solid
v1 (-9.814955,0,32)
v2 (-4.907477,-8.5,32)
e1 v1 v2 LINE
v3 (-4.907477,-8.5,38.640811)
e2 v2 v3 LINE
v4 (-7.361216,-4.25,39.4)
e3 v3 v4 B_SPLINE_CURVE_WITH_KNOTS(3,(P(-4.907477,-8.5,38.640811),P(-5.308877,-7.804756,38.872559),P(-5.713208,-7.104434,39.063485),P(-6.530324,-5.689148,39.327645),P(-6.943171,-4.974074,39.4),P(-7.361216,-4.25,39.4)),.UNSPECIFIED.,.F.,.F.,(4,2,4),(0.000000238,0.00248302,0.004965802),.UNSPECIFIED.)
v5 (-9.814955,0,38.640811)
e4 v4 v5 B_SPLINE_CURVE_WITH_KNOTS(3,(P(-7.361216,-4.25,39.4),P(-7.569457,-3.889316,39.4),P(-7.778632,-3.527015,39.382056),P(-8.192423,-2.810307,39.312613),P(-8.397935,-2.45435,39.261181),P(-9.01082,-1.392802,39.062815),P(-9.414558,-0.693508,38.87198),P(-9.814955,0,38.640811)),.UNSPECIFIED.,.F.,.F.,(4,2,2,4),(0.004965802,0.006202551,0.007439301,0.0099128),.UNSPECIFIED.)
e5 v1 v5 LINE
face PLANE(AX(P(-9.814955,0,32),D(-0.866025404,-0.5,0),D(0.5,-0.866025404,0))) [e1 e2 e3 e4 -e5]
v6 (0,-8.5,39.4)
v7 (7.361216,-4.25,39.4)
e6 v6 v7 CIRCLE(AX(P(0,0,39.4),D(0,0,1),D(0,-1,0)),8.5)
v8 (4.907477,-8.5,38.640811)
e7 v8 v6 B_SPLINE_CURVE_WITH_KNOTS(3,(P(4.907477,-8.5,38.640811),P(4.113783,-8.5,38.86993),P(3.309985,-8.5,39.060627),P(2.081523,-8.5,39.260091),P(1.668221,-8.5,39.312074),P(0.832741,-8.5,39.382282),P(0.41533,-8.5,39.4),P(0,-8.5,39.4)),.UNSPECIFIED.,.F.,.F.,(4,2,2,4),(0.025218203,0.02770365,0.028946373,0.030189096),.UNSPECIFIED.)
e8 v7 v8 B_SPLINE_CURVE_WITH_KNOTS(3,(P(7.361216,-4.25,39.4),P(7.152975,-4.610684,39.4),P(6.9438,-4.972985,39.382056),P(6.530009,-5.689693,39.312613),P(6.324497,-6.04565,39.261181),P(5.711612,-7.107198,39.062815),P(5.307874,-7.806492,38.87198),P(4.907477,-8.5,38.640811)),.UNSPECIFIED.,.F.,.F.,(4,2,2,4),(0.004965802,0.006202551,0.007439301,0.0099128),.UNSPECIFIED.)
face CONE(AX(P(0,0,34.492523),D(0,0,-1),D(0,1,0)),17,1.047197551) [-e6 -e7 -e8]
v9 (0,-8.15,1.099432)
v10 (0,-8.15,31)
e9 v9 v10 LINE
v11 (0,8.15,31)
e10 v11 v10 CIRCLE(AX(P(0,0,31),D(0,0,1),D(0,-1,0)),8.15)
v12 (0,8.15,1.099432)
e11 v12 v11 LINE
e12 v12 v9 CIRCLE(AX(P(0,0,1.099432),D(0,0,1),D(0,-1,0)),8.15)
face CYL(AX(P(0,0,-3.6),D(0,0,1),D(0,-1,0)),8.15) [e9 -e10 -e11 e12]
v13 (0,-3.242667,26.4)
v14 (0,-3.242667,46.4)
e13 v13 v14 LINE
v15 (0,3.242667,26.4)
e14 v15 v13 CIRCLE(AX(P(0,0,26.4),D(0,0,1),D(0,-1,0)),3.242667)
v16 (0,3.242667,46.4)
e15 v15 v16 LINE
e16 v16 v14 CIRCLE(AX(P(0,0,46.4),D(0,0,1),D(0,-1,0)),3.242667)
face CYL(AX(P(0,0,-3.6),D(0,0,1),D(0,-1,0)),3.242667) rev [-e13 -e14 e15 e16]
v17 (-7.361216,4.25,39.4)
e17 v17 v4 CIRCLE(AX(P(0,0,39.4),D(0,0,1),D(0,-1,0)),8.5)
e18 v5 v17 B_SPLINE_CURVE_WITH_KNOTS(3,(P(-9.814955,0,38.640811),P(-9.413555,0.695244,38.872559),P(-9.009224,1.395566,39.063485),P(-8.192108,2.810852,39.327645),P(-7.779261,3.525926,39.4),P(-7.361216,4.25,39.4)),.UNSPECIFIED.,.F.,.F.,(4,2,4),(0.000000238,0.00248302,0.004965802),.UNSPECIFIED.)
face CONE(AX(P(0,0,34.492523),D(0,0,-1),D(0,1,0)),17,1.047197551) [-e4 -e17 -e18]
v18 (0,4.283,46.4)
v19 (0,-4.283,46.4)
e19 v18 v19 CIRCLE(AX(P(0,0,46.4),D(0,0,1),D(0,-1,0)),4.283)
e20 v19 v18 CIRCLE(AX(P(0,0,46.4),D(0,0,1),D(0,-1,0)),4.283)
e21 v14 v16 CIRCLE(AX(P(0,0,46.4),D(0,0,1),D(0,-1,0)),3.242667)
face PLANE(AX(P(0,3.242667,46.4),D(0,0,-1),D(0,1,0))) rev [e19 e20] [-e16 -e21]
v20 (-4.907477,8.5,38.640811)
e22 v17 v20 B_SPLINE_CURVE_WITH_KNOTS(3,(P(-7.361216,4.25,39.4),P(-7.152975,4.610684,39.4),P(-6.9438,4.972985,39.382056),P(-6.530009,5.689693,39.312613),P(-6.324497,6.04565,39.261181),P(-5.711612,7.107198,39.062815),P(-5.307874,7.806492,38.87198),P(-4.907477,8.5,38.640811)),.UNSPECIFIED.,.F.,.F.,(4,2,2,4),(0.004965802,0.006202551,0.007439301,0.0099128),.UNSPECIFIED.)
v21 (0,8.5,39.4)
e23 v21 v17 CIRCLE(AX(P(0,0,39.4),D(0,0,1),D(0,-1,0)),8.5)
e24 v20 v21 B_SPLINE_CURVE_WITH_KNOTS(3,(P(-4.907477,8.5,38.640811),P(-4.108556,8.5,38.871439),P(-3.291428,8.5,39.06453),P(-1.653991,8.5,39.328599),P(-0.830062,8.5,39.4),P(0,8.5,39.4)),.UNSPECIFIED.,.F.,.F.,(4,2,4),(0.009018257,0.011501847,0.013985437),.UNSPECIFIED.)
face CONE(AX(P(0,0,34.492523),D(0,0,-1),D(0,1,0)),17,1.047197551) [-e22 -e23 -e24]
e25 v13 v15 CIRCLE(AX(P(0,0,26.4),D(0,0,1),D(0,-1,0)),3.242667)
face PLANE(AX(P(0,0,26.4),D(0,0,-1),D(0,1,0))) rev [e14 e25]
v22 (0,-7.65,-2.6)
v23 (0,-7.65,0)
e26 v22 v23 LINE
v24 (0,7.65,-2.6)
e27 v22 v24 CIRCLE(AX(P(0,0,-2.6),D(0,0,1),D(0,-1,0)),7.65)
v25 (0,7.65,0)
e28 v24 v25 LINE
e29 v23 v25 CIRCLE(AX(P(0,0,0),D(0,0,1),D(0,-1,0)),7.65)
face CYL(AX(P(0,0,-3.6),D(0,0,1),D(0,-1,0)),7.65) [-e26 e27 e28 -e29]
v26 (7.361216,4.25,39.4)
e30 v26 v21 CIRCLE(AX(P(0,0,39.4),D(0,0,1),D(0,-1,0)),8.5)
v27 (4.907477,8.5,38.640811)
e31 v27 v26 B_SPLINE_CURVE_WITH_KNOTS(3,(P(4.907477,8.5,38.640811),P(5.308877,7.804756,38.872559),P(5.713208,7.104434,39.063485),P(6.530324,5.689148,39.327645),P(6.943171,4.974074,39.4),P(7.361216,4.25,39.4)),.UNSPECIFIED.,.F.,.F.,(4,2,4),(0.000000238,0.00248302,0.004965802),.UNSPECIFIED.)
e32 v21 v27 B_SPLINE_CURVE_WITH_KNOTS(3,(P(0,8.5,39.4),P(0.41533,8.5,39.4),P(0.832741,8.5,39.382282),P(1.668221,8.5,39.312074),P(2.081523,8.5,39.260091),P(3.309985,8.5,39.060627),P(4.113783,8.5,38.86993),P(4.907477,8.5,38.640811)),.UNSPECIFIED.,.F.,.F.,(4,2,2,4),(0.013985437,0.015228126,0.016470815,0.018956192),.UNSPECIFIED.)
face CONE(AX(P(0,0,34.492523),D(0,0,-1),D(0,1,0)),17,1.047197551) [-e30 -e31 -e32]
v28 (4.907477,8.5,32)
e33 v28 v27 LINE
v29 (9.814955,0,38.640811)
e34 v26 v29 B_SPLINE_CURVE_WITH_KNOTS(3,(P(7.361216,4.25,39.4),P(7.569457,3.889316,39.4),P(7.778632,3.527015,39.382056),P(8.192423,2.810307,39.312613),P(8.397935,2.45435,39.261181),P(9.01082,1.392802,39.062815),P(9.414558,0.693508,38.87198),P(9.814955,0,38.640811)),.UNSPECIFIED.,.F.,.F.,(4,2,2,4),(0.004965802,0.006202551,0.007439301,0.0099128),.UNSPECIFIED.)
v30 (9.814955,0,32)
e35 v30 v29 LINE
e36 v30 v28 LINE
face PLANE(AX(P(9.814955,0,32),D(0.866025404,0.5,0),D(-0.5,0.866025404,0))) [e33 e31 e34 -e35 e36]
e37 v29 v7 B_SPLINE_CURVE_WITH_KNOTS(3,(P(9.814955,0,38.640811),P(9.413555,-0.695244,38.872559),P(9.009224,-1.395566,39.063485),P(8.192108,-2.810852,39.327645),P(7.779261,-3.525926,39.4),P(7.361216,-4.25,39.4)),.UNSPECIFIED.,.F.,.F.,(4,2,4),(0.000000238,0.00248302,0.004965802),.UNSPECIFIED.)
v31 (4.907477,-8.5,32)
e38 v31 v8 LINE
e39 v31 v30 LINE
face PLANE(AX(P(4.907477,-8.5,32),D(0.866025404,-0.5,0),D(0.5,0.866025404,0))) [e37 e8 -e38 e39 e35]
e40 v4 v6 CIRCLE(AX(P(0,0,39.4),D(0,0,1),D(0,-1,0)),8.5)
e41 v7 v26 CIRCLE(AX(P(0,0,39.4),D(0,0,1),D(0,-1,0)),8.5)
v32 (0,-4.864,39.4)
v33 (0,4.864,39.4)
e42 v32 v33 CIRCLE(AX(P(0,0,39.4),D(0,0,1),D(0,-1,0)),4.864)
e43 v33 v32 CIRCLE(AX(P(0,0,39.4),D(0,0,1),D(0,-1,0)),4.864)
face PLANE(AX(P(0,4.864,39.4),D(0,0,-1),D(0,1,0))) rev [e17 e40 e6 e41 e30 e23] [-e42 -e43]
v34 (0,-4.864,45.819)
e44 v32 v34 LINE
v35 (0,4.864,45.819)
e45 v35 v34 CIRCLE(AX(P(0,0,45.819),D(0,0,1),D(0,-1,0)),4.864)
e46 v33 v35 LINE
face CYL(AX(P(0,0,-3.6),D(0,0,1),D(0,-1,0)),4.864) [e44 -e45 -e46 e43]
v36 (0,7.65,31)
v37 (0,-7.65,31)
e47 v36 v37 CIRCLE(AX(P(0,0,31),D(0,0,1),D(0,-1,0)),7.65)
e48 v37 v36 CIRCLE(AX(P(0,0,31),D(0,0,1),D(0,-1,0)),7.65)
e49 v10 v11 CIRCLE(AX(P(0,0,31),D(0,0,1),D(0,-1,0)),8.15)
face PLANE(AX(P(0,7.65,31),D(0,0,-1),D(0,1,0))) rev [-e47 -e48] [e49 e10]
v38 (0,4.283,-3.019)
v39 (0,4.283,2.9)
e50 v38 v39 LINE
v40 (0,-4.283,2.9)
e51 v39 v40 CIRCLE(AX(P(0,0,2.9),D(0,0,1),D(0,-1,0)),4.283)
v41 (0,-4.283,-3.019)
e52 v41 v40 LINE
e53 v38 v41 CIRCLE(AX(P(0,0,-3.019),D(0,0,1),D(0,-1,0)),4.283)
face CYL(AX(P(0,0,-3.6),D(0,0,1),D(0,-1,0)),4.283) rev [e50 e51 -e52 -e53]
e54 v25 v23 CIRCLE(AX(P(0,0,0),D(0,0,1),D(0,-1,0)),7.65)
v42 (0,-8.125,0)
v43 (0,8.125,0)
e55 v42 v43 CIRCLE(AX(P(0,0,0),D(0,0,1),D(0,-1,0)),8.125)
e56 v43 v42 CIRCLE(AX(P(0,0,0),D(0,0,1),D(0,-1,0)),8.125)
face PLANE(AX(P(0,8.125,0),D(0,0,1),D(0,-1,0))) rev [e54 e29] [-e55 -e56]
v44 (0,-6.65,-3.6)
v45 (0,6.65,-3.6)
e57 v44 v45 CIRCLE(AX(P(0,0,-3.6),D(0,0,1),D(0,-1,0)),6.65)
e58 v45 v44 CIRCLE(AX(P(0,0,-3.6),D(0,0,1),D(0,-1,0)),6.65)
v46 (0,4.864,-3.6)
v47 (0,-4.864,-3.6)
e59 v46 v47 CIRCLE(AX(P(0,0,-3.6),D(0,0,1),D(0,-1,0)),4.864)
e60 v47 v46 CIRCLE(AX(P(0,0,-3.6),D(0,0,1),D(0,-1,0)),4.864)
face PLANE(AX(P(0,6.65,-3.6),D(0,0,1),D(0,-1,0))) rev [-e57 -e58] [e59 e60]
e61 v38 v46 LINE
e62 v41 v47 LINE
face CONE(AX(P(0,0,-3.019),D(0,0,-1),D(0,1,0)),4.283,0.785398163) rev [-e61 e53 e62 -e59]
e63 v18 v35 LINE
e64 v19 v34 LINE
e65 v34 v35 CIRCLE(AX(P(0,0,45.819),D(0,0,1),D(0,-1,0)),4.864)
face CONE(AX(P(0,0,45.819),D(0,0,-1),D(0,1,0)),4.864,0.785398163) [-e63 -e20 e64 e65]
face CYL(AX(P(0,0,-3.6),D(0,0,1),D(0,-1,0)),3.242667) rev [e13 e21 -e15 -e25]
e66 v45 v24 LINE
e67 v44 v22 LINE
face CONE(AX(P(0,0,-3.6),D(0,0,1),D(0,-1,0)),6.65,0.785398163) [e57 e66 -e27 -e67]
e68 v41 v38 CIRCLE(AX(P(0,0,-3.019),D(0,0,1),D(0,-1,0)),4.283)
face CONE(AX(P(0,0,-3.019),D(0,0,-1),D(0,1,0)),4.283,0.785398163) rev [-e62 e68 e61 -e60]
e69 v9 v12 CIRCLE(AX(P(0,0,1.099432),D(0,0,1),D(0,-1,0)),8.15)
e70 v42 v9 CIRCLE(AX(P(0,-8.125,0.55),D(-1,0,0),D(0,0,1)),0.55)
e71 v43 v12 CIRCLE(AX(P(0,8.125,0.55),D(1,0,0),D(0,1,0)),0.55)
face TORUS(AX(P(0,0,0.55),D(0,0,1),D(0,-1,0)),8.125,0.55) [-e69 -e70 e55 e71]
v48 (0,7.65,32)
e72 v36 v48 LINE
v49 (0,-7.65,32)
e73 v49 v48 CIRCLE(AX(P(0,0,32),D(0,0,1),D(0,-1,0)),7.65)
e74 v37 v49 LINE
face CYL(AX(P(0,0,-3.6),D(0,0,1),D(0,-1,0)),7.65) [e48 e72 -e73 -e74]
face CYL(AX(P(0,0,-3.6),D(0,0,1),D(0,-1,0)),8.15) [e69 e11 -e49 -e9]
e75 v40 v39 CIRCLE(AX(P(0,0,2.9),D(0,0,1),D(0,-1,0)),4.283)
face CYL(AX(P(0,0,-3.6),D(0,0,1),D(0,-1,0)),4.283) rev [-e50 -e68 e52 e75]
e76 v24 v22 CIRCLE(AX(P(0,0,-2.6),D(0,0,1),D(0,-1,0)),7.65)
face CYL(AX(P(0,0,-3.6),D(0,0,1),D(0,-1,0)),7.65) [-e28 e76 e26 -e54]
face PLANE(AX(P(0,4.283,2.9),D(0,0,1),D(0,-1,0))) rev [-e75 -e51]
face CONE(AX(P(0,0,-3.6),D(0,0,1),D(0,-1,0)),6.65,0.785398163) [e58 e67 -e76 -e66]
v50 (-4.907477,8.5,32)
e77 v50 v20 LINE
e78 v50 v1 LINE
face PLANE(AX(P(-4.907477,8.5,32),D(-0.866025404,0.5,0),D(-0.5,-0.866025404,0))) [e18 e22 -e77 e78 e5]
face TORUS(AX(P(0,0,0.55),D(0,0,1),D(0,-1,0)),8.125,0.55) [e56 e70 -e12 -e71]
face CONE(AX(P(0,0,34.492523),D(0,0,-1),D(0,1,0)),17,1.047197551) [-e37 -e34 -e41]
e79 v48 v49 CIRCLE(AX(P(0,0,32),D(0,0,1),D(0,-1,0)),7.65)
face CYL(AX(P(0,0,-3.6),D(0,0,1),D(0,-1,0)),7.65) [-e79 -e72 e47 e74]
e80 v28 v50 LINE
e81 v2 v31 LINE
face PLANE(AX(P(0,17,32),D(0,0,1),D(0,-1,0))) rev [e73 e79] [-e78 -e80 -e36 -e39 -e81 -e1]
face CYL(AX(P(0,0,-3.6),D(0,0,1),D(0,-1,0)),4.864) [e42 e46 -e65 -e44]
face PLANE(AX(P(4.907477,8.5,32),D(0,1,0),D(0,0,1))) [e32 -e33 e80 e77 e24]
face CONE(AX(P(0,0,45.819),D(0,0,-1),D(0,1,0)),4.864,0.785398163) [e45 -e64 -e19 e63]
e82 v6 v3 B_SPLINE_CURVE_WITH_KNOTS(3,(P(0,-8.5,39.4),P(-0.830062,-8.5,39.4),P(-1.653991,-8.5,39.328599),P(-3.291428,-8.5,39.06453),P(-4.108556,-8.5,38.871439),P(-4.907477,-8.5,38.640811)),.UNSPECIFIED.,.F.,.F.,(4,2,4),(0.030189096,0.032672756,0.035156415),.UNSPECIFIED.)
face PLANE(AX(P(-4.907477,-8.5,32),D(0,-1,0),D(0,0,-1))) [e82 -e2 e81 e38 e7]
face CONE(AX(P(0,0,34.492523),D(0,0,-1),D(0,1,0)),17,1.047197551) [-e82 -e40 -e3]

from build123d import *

# Parameters (mm, degrees)
CUT_EXTRUDE_START   = -7.4
SKETCH_2_R          = 17
CUT_EXTRUDE_1_DEPTH = 7.4


with BuildPart() as part:
    # 草图1 → 旋转1 (revolve)
    with BuildSketch(Plane(origin=(0, 0, 0), x_dir=(0, 0, -1), z_dir=(1, 0, 0)), mode=Mode.PRIVATE) as revolve_1_sk:
        with BuildLine():
            Line((-26.4, 0), (-26.4, 3.242666667))
            Line((-26.4, 3.242666667), (-46.4, 3.242666667))
            Line((-46.4, 3.242666667), (-46.4, 4.283))
            Line((-46.4, 4.283), (-45.819, 4.864))
            Line((-45.819, 4.864), (-39.4, 4.864))
            Line((-39.4, 4.864), (-39.4, 8.5))
            Line((-39.4, 8.5), (-34.492522712, 17))
            Line((-34.492522712, 17), (-32, 17))
            Line((-32, 17), (-32, 7.65))
            Line((-32, 7.65), (-31, 7.65))
            Line((-31, 7.65), (-31, 8.15))
            Line((-31, 8.15), (-1.099431524, 8.15))
            ThreePointArc((-1.099431524, 8.15), (-0.537496769, 8.674857863), (0, 8.125))
            Line((0, 8.125), (0, 7.65))
            Line((0, 7.65), (2.6, 7.65))
            Line((2.6, 7.65), (3.6, 6.65))
            Line((3.6, 6.65), (3.6, 4.864))
            Line((3.6, 4.864), (3.019, 4.283))
            Line((3.019, 4.283), (-2.9, 4.283))
            Line((-2.9, 4.283), (-2.9, 0))
            Line((-2.9, 0), (-26.4, 0))
        make_face()
    revolve(revolve_1_sk.sketch.rotate(Axis((0, 0, -3.6), (0, 0, 1)), 180), axis=Axis((0, 0, -3.6), (0, 0, 1)))

    # 草图2 → 切除-拉伸1 (cut)
    with BuildSketch(Plane.XY.offset(39.4).offset(CUT_EXTRUDE_START)):
        Circle(SKETCH_2_R)
        Polygon((-4.907477288, -8.5), (4.907477288, -8.5), (9.814954576, 0), (4.907477288, 8.5), (-4.907477288, 8.5), (-9.814954576, 0), align=None, mode=Mode.SUBTRACT)
    extrude(amount=CUT_EXTRUDE_1_DEPTH, mode=Mode.SUBTRACT)


solid = part.part
